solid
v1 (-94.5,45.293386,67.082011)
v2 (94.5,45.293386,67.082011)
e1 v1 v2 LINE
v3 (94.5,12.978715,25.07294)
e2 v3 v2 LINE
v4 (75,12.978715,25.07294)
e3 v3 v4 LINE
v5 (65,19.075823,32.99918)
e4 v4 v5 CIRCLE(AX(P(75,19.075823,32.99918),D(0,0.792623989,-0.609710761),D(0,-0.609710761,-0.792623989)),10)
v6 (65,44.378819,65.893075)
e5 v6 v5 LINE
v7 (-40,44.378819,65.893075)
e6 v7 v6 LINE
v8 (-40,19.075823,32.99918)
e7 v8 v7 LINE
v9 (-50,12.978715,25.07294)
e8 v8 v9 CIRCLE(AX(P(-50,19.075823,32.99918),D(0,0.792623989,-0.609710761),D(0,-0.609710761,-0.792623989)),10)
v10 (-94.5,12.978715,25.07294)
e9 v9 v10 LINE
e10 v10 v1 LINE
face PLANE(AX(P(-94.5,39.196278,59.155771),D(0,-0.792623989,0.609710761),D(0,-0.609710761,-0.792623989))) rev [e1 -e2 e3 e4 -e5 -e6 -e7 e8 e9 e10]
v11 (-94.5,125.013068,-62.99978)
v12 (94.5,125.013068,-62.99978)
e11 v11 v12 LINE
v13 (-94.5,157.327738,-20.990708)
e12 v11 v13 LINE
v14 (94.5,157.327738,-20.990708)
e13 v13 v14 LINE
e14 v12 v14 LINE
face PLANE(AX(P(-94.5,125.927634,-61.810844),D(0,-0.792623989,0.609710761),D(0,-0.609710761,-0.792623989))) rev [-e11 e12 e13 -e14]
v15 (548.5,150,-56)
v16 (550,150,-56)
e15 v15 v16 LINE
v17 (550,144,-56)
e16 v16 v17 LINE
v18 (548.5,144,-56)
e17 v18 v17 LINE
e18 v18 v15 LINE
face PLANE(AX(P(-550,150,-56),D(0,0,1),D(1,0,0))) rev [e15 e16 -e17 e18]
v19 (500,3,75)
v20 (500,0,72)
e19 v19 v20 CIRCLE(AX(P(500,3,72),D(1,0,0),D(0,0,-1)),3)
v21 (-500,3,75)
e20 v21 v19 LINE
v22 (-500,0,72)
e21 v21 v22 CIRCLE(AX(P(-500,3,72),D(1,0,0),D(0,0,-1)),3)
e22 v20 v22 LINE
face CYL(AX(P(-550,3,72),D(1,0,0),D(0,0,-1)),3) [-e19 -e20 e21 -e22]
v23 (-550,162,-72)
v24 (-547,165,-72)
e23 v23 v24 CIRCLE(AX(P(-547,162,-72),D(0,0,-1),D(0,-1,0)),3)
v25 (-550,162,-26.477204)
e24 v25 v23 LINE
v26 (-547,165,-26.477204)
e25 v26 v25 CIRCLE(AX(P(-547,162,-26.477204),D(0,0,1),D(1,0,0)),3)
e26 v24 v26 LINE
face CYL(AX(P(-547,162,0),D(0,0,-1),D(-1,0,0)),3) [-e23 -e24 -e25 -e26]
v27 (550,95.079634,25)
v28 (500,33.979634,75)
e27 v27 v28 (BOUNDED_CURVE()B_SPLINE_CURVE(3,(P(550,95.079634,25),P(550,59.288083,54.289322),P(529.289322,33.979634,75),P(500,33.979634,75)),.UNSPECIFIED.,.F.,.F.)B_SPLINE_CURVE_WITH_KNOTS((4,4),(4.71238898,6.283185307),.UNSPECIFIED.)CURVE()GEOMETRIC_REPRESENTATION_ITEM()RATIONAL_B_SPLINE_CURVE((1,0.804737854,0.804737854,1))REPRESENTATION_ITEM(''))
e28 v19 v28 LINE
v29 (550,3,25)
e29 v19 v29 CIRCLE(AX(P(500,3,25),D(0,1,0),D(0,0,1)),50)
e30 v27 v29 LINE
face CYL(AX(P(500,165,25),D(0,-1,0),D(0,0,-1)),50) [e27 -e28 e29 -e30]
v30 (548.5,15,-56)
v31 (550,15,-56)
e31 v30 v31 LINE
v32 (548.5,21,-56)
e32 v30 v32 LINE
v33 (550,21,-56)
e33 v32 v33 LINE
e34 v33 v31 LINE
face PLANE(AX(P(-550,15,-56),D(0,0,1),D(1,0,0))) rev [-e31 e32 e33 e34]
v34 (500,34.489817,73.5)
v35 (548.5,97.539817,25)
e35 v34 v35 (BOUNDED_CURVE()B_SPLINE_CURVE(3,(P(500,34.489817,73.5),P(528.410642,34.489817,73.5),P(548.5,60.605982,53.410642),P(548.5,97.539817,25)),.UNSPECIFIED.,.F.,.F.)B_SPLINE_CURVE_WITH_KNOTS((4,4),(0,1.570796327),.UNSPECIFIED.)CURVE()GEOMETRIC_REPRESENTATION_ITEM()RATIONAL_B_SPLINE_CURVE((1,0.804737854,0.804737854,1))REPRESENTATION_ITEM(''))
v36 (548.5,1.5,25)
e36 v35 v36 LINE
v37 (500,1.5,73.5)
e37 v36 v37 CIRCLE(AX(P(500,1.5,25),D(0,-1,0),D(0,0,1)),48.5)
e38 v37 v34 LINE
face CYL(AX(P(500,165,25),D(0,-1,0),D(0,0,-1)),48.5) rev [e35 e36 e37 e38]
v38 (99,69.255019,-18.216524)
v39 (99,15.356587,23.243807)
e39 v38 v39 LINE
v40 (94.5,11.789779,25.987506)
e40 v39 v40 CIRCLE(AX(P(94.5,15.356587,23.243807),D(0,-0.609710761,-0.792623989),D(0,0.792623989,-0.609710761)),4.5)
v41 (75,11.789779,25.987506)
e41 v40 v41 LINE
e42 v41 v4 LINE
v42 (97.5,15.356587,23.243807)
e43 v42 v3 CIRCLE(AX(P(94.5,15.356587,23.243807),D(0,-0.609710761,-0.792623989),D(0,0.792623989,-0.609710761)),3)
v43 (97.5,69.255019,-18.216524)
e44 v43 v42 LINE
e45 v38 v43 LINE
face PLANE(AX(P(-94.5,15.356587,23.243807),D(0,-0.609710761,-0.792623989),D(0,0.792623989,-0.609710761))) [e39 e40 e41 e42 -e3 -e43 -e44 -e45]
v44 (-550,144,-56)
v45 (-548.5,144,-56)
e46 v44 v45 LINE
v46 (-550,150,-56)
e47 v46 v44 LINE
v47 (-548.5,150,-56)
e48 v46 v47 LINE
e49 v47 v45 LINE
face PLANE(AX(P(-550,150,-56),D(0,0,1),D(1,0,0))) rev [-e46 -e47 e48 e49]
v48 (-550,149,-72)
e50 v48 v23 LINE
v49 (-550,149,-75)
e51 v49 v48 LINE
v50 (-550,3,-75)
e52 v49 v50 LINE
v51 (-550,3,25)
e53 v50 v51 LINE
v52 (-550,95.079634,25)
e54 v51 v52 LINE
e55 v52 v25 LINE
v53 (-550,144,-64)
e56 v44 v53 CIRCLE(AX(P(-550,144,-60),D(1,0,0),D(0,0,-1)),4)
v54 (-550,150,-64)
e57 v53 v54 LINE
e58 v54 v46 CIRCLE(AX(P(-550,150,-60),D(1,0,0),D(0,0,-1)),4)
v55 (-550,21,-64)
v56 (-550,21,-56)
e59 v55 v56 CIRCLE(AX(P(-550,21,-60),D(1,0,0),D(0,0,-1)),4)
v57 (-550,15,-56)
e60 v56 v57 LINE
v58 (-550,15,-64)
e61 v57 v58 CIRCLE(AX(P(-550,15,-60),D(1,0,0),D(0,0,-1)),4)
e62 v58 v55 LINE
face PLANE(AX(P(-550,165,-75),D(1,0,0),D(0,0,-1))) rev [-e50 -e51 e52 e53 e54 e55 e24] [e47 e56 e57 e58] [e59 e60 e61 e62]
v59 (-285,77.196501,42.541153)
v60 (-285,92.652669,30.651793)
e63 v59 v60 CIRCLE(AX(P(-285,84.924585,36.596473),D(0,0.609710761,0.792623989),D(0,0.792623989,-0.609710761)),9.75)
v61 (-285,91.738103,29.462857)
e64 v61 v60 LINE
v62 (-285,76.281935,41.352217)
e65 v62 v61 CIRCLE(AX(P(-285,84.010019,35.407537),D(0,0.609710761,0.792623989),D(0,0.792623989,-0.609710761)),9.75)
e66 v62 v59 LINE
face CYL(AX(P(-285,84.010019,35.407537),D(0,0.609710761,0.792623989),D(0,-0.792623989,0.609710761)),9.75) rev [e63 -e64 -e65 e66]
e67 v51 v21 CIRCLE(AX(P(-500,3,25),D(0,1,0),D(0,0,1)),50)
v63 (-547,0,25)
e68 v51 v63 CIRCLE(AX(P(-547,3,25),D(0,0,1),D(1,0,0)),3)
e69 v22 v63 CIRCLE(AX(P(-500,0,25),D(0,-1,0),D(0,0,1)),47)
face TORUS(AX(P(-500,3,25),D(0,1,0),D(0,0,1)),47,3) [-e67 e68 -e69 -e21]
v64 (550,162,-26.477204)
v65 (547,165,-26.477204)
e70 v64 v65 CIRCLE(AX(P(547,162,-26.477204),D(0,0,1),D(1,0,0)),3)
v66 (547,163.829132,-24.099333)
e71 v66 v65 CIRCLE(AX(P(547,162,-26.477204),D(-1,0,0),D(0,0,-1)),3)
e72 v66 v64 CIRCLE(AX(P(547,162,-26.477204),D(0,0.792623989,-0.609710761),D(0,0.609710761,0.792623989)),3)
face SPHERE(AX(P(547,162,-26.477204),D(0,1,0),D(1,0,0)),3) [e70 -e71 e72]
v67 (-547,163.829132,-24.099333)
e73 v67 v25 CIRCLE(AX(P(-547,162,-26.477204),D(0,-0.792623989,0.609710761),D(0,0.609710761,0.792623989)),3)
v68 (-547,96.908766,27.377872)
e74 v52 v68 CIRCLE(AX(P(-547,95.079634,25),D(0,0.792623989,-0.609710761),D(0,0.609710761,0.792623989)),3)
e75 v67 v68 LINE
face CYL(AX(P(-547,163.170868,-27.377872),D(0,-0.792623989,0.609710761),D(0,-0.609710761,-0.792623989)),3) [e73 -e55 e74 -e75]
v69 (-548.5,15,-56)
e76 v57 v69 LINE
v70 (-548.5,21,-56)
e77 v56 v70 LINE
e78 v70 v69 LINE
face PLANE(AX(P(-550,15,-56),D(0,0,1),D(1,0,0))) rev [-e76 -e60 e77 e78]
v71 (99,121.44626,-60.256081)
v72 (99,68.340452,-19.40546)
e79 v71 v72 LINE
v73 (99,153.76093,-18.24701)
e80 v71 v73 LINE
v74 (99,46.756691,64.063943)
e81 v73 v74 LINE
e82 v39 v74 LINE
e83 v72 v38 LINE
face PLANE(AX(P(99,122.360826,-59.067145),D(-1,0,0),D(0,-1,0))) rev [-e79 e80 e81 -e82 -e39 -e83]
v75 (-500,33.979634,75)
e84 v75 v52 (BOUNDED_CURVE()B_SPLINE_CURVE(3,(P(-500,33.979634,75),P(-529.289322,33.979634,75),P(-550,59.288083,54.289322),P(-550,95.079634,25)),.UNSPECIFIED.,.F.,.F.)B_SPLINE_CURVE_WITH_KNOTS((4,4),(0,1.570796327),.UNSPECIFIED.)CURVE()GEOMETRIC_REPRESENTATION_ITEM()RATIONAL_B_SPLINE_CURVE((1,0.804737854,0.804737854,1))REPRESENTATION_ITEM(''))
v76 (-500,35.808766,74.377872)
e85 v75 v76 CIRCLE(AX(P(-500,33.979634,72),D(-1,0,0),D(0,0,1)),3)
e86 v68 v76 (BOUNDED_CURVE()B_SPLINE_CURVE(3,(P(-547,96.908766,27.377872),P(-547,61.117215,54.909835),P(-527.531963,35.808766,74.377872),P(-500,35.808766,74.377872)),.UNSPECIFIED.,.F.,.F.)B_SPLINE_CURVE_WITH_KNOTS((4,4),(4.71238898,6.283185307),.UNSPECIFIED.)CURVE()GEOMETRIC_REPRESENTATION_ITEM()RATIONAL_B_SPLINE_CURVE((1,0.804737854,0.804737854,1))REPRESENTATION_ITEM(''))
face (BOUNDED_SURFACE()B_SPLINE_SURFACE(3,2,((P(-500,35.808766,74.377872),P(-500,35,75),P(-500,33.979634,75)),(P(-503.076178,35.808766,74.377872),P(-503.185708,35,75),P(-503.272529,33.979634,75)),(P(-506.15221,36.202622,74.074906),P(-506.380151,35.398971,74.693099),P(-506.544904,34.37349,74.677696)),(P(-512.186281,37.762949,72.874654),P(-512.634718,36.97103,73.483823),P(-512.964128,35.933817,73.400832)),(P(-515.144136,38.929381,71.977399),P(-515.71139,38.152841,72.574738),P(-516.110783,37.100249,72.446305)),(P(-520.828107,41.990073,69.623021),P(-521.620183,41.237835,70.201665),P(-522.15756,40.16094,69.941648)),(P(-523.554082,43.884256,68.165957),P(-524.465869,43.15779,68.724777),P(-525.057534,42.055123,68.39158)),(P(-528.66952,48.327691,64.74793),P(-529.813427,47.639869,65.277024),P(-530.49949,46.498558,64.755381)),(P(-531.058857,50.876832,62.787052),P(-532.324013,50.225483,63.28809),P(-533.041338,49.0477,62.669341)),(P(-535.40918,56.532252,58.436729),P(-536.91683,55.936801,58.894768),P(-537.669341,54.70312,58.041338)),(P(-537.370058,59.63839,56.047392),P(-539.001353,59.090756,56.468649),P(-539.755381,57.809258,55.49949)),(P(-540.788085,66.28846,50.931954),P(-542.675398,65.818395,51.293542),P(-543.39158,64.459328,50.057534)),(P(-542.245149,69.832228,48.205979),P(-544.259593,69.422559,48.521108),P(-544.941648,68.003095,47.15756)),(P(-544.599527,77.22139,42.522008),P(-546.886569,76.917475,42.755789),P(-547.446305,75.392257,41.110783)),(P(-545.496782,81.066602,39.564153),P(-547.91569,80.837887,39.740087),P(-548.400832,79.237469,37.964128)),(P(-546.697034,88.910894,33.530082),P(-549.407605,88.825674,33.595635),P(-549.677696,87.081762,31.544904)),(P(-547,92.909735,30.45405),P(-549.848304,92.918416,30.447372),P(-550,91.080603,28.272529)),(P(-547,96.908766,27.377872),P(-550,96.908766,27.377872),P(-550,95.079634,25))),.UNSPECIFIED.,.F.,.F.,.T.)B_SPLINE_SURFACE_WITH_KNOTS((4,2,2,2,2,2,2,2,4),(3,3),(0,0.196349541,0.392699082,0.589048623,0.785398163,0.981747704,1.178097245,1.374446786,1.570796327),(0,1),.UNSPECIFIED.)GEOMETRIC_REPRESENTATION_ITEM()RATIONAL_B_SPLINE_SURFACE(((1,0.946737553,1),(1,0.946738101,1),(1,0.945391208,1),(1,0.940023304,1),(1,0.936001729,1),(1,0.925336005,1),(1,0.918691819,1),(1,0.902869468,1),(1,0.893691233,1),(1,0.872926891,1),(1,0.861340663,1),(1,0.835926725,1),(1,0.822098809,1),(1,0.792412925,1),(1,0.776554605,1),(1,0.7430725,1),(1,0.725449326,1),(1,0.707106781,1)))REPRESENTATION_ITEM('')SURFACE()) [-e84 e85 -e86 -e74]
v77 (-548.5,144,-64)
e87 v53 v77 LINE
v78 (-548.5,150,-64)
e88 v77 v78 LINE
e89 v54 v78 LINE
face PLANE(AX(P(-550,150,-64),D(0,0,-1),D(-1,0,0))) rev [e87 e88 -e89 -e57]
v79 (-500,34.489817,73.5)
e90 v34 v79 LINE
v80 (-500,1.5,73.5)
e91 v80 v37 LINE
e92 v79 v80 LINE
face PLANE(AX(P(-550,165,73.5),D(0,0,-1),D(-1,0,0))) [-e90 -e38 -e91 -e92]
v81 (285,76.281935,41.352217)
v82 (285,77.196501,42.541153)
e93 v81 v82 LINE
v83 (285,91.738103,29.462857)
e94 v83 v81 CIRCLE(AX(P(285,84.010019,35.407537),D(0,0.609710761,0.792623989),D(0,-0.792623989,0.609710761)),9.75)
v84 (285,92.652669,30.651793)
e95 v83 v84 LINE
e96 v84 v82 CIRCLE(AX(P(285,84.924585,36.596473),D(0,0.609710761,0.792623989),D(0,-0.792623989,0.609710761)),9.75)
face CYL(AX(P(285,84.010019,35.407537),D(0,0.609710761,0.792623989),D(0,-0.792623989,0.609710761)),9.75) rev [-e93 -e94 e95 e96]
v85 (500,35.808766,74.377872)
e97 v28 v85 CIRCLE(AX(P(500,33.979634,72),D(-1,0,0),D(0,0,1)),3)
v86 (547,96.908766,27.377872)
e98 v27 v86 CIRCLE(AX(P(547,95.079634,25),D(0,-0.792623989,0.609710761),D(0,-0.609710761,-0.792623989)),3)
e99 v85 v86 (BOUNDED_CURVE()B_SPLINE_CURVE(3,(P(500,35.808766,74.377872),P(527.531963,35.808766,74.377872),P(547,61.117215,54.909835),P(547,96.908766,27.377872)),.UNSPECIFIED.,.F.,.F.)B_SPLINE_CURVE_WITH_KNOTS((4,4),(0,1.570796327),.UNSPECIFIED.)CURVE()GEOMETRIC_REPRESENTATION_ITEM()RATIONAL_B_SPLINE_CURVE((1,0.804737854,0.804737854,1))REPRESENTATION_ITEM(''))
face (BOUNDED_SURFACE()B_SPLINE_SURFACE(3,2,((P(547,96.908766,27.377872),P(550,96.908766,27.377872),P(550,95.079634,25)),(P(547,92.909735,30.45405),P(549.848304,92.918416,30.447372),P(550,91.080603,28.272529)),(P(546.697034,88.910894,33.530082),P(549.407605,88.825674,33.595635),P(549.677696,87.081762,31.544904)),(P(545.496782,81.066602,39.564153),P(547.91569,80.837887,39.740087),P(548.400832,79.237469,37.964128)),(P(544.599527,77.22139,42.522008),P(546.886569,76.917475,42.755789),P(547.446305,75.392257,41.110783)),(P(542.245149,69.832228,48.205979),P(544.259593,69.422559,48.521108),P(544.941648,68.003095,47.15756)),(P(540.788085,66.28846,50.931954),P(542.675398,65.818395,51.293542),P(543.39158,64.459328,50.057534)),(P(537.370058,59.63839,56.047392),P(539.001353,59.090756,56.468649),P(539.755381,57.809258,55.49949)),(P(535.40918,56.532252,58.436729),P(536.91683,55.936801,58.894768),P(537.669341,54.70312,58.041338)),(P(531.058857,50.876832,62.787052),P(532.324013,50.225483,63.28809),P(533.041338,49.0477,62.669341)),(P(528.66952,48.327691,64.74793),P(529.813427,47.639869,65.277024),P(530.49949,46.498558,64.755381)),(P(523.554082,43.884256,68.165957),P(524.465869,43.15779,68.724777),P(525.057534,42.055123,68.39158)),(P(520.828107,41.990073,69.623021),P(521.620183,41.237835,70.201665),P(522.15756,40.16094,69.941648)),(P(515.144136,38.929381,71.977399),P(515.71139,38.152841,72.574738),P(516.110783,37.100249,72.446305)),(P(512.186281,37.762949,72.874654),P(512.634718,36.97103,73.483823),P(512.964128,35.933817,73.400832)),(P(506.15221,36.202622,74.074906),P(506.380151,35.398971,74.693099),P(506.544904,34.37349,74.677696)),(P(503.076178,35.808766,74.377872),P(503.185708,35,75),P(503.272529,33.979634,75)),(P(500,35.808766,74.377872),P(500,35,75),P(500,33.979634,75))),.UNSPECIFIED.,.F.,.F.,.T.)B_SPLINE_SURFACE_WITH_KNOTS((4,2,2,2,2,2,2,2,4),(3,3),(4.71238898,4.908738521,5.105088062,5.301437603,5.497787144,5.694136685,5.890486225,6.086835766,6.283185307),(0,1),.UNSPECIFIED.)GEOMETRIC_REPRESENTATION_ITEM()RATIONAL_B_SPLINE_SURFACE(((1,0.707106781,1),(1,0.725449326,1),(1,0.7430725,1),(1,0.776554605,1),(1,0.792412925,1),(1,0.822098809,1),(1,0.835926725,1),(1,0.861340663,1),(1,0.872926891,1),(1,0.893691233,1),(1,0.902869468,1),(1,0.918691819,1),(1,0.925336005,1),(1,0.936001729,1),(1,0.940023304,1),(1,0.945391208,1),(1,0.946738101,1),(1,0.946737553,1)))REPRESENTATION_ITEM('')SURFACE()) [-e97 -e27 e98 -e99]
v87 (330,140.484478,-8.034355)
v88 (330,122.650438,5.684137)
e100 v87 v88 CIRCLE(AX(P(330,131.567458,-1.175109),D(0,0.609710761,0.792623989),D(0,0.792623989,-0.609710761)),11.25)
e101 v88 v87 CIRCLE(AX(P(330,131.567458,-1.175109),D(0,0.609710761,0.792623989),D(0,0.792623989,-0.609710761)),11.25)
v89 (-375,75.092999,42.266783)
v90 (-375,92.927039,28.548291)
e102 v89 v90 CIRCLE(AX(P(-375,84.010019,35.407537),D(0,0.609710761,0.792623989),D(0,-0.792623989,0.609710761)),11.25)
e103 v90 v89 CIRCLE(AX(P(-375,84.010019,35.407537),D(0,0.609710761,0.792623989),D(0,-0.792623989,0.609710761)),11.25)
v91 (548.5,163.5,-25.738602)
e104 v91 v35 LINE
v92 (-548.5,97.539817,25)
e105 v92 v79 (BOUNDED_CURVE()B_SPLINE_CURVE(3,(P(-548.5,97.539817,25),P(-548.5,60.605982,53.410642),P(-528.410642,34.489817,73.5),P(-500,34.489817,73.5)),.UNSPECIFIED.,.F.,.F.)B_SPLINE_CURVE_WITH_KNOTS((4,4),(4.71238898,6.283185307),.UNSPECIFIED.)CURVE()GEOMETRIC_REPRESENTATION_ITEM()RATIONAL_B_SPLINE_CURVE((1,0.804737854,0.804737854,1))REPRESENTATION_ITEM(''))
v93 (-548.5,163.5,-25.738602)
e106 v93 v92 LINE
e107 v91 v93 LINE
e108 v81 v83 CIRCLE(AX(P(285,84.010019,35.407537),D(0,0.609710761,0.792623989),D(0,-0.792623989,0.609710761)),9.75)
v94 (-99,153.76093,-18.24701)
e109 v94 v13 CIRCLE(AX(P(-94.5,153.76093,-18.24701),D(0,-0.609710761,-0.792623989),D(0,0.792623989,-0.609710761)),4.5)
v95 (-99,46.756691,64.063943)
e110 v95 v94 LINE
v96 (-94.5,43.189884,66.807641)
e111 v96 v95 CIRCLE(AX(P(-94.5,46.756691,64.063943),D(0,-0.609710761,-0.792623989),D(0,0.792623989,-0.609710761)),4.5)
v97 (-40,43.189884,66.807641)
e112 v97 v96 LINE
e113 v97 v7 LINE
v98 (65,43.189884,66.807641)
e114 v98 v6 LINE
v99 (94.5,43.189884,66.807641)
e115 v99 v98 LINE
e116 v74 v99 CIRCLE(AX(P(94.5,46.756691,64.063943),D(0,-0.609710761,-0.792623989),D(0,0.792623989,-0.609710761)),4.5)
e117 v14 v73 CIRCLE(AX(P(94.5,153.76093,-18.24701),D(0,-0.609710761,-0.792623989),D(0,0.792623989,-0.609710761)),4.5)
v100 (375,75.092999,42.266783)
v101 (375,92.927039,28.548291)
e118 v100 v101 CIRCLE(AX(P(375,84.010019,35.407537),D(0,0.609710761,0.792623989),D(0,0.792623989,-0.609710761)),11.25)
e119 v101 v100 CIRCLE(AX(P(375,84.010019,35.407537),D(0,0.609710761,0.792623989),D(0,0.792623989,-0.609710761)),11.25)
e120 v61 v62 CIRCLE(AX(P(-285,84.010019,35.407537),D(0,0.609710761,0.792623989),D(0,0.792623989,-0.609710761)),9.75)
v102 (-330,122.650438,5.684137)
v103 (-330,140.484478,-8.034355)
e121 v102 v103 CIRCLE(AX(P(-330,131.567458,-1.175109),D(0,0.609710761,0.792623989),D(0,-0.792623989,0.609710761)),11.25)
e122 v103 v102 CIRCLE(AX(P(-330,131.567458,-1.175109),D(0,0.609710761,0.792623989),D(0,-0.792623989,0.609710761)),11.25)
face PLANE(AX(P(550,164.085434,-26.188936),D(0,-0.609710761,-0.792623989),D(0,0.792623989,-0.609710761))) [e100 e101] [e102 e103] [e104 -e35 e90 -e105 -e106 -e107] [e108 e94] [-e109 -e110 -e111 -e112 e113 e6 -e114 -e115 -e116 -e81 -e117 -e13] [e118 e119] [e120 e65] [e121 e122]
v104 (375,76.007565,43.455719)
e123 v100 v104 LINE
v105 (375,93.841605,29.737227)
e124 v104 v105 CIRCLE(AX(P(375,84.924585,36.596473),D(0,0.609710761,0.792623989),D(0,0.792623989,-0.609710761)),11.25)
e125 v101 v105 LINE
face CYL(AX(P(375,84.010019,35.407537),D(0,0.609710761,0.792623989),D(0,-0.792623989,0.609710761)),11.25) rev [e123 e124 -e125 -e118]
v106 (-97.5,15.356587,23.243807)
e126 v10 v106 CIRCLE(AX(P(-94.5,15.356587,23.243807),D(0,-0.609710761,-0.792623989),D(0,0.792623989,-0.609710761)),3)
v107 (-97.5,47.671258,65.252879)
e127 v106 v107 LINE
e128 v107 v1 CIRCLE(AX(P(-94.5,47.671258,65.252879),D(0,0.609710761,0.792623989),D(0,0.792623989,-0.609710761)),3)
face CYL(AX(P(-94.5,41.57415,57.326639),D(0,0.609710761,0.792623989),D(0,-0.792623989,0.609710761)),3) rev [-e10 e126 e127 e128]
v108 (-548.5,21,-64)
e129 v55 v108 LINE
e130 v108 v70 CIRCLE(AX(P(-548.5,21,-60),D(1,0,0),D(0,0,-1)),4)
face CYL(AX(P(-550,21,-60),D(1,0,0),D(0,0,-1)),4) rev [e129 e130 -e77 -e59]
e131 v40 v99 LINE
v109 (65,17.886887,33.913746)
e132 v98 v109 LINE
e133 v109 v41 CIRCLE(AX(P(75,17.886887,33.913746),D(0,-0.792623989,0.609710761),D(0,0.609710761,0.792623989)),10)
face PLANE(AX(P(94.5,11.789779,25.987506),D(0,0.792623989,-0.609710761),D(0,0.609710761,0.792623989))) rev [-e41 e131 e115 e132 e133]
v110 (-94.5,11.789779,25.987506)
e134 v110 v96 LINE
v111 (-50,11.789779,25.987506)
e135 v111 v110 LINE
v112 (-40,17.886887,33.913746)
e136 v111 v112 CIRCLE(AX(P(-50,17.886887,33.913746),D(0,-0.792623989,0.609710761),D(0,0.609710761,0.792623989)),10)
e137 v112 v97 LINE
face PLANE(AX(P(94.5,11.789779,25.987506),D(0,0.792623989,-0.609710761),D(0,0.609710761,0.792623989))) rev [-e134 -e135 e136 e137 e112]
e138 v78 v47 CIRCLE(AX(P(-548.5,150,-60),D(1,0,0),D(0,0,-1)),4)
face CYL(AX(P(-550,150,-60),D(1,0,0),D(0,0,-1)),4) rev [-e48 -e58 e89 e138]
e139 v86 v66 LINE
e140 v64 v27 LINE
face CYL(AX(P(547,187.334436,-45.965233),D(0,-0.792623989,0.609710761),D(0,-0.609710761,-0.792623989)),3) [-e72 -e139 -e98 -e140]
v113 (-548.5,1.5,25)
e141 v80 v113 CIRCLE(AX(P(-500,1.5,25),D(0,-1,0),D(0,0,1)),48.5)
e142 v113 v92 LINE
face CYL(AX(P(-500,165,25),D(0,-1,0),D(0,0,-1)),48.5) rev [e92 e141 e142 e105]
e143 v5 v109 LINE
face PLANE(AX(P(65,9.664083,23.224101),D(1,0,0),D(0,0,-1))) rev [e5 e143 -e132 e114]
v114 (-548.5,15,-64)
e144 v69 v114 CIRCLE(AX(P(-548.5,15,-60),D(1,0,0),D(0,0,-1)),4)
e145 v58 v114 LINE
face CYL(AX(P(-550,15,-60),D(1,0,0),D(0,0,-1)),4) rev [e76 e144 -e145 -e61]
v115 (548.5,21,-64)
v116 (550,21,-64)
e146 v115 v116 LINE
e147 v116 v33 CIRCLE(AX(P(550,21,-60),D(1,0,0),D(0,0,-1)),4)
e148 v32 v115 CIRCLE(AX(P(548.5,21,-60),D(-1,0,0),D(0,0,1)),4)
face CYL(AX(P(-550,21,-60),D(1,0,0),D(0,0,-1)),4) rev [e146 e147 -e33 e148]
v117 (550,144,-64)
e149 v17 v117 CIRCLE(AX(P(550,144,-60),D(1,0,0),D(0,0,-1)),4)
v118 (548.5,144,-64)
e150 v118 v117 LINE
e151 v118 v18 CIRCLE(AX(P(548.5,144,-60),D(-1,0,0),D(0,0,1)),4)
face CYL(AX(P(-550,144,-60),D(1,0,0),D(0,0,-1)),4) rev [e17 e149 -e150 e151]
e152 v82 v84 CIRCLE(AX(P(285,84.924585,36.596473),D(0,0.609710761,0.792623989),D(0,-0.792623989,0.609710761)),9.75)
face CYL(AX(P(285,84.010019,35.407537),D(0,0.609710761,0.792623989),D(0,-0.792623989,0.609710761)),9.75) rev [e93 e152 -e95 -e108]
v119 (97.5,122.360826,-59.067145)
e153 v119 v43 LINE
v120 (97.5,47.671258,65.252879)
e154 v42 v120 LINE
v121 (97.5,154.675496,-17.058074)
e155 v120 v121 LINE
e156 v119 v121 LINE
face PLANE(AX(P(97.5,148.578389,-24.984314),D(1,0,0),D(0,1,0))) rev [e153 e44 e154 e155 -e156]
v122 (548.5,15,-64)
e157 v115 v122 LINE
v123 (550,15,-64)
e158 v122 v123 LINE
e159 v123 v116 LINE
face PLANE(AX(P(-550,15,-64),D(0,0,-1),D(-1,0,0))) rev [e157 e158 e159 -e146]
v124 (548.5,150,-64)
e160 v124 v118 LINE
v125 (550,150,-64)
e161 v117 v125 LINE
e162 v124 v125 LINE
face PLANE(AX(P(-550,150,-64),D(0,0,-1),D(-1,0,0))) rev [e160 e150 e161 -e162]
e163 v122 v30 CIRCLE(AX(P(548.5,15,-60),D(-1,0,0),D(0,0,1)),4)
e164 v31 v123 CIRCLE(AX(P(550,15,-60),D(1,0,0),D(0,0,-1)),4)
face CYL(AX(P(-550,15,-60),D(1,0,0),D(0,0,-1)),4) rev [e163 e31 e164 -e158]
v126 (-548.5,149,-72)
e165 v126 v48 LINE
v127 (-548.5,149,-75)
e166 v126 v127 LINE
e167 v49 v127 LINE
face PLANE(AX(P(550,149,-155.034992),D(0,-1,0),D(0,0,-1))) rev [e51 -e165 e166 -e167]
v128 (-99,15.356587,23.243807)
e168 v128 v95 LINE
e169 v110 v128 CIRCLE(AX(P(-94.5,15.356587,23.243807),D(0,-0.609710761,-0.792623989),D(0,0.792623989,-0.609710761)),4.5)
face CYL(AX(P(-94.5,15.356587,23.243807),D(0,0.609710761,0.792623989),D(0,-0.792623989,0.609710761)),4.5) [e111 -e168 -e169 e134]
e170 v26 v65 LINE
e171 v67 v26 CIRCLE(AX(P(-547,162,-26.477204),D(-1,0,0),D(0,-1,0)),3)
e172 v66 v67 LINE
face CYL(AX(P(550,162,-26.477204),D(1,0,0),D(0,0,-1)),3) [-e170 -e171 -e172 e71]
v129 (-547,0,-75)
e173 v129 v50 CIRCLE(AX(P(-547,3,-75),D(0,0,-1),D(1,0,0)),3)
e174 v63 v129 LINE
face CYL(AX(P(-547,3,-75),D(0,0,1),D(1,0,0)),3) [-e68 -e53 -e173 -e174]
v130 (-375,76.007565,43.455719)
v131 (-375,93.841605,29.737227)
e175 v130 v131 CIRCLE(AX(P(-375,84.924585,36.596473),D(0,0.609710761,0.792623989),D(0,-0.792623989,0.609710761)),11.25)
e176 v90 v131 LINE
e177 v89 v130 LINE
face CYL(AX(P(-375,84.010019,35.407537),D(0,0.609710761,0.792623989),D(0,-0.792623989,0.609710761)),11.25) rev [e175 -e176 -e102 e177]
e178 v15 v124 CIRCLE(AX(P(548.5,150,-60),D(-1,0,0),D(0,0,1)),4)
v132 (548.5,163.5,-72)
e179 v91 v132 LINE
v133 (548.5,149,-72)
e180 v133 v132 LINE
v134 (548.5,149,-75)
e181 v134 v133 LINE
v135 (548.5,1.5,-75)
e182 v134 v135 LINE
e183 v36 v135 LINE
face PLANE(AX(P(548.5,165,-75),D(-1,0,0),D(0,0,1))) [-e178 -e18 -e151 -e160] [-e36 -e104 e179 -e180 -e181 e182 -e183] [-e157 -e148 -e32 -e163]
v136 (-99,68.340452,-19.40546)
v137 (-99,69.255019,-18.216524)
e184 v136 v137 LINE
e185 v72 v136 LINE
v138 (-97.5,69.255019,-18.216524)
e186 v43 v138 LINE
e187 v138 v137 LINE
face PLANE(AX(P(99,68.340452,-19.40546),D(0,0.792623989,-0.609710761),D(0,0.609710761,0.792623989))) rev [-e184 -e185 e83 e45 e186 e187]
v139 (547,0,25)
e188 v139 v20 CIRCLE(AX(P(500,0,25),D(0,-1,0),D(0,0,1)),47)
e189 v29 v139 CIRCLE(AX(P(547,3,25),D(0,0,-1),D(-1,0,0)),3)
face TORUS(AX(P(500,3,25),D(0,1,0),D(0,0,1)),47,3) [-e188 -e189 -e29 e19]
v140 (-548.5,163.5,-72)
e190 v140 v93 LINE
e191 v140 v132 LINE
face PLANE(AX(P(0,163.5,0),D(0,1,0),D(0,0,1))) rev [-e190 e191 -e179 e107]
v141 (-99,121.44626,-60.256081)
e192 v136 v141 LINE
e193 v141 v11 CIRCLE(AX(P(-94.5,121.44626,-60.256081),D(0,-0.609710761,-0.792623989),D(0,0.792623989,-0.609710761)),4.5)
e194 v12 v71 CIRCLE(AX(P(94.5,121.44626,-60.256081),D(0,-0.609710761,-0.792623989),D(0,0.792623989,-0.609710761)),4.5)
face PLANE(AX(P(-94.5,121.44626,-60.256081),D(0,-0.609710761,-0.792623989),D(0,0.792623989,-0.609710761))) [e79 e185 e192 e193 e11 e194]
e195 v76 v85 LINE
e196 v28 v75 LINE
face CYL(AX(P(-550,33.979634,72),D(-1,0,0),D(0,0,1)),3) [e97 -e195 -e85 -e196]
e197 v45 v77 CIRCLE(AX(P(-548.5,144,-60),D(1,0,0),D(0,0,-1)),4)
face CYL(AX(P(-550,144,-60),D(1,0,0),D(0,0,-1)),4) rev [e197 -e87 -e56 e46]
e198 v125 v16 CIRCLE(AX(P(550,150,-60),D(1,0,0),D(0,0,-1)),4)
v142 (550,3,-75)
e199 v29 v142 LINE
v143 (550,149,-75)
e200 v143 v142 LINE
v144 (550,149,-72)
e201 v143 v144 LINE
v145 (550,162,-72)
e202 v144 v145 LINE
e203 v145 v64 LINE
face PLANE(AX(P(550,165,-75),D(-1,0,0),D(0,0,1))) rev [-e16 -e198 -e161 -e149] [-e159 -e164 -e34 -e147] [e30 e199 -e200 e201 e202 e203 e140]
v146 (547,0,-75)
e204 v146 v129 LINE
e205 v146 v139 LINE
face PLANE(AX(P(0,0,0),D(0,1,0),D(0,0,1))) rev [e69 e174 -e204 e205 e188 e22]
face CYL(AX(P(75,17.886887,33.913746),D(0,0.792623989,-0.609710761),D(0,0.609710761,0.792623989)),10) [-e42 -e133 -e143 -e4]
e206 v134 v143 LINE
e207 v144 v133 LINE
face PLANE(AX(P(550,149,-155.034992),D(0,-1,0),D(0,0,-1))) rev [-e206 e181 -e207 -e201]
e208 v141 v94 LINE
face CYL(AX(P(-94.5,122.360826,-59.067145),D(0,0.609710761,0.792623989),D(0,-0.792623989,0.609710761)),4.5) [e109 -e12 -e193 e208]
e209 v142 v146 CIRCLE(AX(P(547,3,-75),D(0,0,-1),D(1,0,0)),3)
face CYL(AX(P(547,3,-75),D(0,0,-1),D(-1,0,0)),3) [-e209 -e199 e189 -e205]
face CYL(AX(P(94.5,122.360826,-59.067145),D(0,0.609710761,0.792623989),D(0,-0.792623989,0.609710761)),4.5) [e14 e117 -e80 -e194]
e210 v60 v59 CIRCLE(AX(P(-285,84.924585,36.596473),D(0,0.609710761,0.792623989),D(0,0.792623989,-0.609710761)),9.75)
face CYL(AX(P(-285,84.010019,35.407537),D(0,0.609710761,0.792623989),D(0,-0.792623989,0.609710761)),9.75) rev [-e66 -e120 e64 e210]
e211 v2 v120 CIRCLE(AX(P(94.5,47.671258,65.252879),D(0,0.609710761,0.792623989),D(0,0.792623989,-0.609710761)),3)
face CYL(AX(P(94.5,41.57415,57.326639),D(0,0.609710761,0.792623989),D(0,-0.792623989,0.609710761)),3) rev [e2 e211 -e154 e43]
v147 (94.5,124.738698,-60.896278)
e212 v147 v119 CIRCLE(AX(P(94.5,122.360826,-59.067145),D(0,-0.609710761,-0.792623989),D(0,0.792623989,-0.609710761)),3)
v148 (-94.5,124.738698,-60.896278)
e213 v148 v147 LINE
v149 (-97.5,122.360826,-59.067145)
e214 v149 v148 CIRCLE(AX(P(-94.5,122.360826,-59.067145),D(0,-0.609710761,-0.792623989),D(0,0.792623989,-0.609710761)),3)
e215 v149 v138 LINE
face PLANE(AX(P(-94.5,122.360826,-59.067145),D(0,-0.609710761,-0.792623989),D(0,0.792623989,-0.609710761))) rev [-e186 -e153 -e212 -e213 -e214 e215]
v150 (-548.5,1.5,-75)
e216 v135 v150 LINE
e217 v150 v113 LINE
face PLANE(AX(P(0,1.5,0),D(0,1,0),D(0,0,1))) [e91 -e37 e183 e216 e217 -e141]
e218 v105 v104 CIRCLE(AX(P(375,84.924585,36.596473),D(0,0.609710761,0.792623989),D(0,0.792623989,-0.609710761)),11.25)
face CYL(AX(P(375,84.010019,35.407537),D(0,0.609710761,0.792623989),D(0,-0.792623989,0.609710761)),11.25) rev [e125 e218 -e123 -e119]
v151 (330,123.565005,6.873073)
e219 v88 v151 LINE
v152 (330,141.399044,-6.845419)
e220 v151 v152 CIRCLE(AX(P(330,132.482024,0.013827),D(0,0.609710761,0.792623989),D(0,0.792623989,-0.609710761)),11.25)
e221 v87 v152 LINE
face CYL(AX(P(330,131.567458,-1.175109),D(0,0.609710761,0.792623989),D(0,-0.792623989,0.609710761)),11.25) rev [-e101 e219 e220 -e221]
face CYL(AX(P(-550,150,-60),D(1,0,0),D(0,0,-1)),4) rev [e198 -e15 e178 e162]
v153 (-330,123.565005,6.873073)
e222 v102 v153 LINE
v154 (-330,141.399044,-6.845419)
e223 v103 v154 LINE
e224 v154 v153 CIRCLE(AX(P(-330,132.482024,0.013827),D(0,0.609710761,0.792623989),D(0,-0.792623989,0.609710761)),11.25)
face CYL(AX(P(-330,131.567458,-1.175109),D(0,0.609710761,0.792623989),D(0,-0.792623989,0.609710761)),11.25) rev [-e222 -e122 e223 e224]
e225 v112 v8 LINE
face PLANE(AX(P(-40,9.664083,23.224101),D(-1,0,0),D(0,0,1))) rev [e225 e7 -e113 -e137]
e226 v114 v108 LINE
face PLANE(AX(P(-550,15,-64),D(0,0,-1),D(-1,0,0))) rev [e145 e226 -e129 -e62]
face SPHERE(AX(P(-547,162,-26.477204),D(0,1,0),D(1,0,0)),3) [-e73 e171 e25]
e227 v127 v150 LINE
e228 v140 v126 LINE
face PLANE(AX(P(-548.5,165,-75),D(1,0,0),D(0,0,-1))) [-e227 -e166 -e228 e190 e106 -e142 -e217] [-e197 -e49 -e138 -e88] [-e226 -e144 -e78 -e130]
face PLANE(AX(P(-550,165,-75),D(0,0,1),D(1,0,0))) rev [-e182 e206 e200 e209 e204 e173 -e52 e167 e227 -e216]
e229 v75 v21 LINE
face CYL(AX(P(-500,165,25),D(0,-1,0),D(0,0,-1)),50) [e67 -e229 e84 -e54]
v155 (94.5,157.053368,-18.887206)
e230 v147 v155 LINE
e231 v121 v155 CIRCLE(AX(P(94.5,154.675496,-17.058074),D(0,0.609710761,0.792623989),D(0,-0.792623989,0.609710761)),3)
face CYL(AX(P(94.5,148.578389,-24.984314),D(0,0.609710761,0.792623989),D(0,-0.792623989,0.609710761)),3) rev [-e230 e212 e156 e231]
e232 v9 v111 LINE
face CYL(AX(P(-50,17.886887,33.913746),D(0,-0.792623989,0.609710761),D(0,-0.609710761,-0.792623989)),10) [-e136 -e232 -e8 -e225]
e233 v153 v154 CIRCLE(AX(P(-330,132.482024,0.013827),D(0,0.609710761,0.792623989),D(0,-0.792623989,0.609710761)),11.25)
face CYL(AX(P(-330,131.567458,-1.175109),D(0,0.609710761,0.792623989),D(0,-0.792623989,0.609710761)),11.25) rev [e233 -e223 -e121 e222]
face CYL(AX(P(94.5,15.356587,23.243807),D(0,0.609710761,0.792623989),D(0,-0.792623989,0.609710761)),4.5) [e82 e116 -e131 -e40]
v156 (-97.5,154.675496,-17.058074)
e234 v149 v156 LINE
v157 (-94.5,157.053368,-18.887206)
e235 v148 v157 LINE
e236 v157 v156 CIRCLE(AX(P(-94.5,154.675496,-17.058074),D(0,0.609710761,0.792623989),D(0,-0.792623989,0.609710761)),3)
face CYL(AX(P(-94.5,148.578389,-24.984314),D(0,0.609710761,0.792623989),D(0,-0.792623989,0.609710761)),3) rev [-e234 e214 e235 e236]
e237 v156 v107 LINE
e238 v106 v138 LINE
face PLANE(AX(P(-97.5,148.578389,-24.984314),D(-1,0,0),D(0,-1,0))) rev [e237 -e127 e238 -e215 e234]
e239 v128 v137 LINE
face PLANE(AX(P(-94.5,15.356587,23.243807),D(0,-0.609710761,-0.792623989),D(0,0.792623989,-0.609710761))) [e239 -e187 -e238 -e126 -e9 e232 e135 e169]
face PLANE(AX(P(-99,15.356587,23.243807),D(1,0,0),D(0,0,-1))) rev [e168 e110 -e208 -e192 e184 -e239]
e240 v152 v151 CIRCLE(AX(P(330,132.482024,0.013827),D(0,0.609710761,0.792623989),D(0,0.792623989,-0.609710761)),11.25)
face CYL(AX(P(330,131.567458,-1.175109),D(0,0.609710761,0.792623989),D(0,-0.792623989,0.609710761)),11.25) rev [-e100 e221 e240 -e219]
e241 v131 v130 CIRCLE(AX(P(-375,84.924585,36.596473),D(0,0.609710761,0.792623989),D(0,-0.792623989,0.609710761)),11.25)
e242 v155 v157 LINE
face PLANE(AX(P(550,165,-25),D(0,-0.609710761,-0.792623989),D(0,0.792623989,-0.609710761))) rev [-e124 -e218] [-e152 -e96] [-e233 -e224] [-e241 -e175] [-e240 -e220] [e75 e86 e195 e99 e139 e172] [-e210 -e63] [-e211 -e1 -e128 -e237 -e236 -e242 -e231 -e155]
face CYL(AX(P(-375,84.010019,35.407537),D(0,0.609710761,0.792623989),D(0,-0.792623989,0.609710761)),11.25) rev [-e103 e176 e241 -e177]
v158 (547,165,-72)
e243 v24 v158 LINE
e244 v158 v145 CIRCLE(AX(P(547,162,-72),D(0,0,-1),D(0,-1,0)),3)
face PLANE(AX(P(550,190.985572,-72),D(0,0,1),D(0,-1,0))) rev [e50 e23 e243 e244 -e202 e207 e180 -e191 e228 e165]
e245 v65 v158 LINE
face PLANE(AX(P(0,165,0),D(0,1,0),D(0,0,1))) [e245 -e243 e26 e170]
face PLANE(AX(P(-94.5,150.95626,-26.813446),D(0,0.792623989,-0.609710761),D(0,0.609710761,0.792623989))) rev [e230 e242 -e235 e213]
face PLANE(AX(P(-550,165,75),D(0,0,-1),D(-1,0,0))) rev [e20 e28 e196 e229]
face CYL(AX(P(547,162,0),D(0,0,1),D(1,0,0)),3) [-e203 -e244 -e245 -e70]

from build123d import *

# Parameters (mm, degrees)
SKETCH_1_W            = 1100
SKETCH_1_H            = 150
EXTRUDE_1_DEPTH       = 165
CUT_EXTRUDE_8_DEPTH   = 1115.831825882
FILLET_2_R            = 50
SHELL_1_T             = -1.5
HOLE_WIZARD_8_0_8_1_D = 8
SKETCH_20_W           = 83.034991693
SKETCH_20_H           = 41.985572191
CUT_EXTRUDE_7_DEPTH   = 1115.831825882
FILLET_5_R            = 3
CUT_EXTRUDE_10_DEPTH  = 1115.831825988
CUT_EXTRUDE_11_DEPTH  = 10
EXTRUDE_2_DEPTH       = 51.5
EXTRUDE_3_DEPTH       = 1.5
SKETCH_27_W           = 130
SKETCH_27_H           = 54.986401043
CUT_EXTRUDE_12_DEPTH  = 1.5
MOVE_FACE_1_BY        = 25
FILLET_6_R            = 10
SKETCH_28_R           = 11.25
SKETCH_28_R_2         = 9.75
CUT_EXTRUDE_13_DEPTH  = 1.5


with BuildPart() as part:
    # 草图1 → 凸台-拉伸1 (new body)
    with BuildSketch(Plane(origin=(0, 0, 0), x_dir=(1, 0, 0), z_dir=(0, 1, 0))):
        Rectangle(SKETCH_1_W, SKETCH_1_H)
    extrude(amount=EXTRUDE_1_DEPTH)

    # 草图21 → 切除-拉伸8 (cut, through all)
    with BuildSketch(Plane.ZY.offset(550)):
        Polygon((-25, 165), (75, 35), (149.01608628, 35), (149.01608628, 165), align=None)
    extrude(amount=-CUT_EXTRUDE_8_DEPTH, mode=Mode.SUBTRACT)

    # 圆角2
    fillet_2_edges = [part.edges().sort_by_distance(p)[0] for p in [
        (550, 17.5, 75),
        (-550, 17.5, 75),
    ]]
    fillet(fillet_2_edges, radius=FILLET_2_R)

    # 抽壳1
    shell_1_openings = [part.faces().sort_by_distance(p)[0] for p in [
        (0, 82.5, -75),
    ]]
    offset(amount=SHELL_1_T, openings=shell_1_openings, kind=Kind.INTERSECTION)

    # Ø8.0 (8) 直径孔1 (through all)
    with Locations(Plane.ZY.offset(550)):
        with Locations((-60, 147), (-60, 18)):
            Hole(HOLE_WIZARD_8_0_8_1_D / 2)

    # 草图20 → 切除-拉伸7 (cut, through all)
    with BuildSketch(Plane.ZY.offset(550)):
        with Locations((-113.517495847, 169.992786096)):
            Rectangle(SKETCH_20_W, SKETCH_20_H)
    extrude(amount=-CUT_EXTRUDE_7_DEPTH, mode=Mode.SUBTRACT)

    # 圆角5
    fillet_5_edges = [part.edges().sort_by_distance(p)[0] for p in [
        (550, 165, -48.5),
        (0, 165, -25),
        (-550, 132.5, 0),
        (550, 132.5, 0),
        (550, 0, -25),
        (0, 0, 75),
        (-535.355339059, 0, 60.355339059),
        (535.355339059, 0, 60.355339059),
        (0, 35, 75),
        (-539.140260323, 59.552655996, 56.113341541),
        (539.140260323, 59.552655996, 56.113341541),
        (-550, 0, -25),
        (-550, 165, -48.5),
    ]]
    fillet(fillet_5_edges, radius=FILLET_5_R)

    # 草图23 → 切除-拉伸10 (cut, through all)
    with BuildSketch(Plane(origin=(550, 0, 0), x_dir=(0, 0, -1), z_dir=(1, 0, 0))):
        with BuildLine():
            Line((64, 150), (64, 144))
            ThreePointArc((64, 144), (60, 140), (56, 144))
            Line((56, 144), (56, 150))
            ThreePointArc((56, 150), (60, 154), (64, 150))
        make_face()
        with BuildLine():
            Line((56, 15), (56, 21))
            ThreePointArc((56, 21), (60, 25), (64, 21))
            Line((64, 21), (64, 15))
            ThreePointArc((64, 15), (60, 11), (56, 15))
        make_face()
    extrude(amount=-CUT_EXTRUDE_10_DEPTH, mode=Mode.SUBTRACT)

    # 草图24 → 切除-拉伸11 (cut)
    with BuildSketch(Plane(origin=(0, 49.256505576, 64.033457249), x_dir=(1, 0, 0), z_dir=(0, 0.6097107608496924, 0.7926239891046002))):
        with BuildLine():
            Line((-94.5, 136), (94.5, 136))
            ThreePointArc((94.5, 136), (96.621320344, 135.121320344), (97.5, 133))
            Line((97.5, 133), (97.5, -2))
            ThreePointArc((97.5, -2), (96.621320344, -4.121320344), (94.5, -5))
            Line((94.5, -5), (-94.5, -5))
            ThreePointArc((-94.5, -5), (-96.621320344, -4.121320344), (-97.5, -2))
            Line((-97.5, -2), (-97.5, 133))
            ThreePointArc((-97.5, 133), (-96.621320344, 135.121320344), (-94.5, 136))
        make_face()
    extrude(amount=-CUT_EXTRUDE_11_DEPTH, mode=Mode.SUBTRACT)

    # 草图25 → 凸台-拉伸2 (add)
    with BuildSketch(Plane(origin=(0, 48.341939435, 62.844521265), x_dir=(-1, 0, 0), z_dir=(0, -0.6097107608496924, -0.7926239891046002))):
        with BuildLine():
            Line((99, -2), (99, 133))
            ThreePointArc((99, 133), (97.681980515, 136.181980515), (94.5, 137.5))
            Line((94.5, 137.5), (-94.5, 137.5))
            ThreePointArc((-94.5, 137.5), (-97.681980515, 136.181980515), (-99, 133))
            Line((-99, 133), (-99, -2))
            ThreePointArc((-99, -2), (-97.681980515, -5.181980515), (-94.5, -6.5))
            Line((-94.5, -6.5), (94.5, -6.5))
            ThreePointArc((94.5, -6.5), (97.681980515, -5.181980515), (99, -2))
        make_face()
        with BuildLine():
            Line((94.5, 136), (-94.5, 136))
            ThreePointArc((-94.5, 136), (-96.621320344, 135.121320344), (-97.5, 133))
            Line((-97.5, 133), (-97.5, -2))
            ThreePointArc((-97.5, -2), (-96.621320344, -4.121320344), (-94.5, -5))
            Line((-94.5, -5), (94.5, -5))
            ThreePointArc((94.5, -5), (96.621320344, -4.121320344), (97.5, -2))
            Line((97.5, -2), (97.5, 133))
            ThreePointArc((97.5, 133), (96.621320344, 135.121320344), (94.5, 136))
        make_face(mode=Mode.SUBTRACT)
    extrude(amount=EXTRUDE_2_DEPTH)

    # 草图26 → 凸台-拉伸3 (add)
    with BuildSketch(Plane(origin=(0, 16.941835251, 22.024385827), x_dir=(-1, 0, 0), z_dir=(0, -0.6097107608496924, -0.7926239891046002))):
        with BuildLine():
            Line((-99, 66), (99, 66))
            Line((99, 66), (99, 133))
            ThreePointArc((99, 133), (97.681980515, 136.181980515), (94.5, 137.5))
            Line((94.5, 137.5), (-94.5, 137.5))
            ThreePointArc((-94.5, 137.5), (-97.681980515, 136.181980515), (-99, 133))
            Line((-99, 133), (-99, 66))
        make_face()
    extrude(amount=EXTRUDE_3_DEPTH)

    # 草图27 → 切除-拉伸12 (cut)
    with BuildSketch(Plane(origin=(0, -3.963119946, 3.048553804), x_dir=(1, 0, 0), z_dir=(0, 0.7926239891046, -0.6097107608496924))):
        with Locations((0, -51.793475292)):
            Rectangle(SKETCH_27_W, SKETCH_27_H)
    extrude(amount=-CUT_EXTRUDE_12_DEPTH, mode=Mode.SUBTRACT)

    # Move Face 1: a face moved outward by 25.0
    extrude(part.faces().sort_by_distance((-65, 28.084299406, 45.940290421))[0], amount=MOVE_FACE_1_BY, dir=(1, 0, 0))

    # 圆角6
    fillet_6_edges = [part.edges().sort_by_distance(p)[0] for p in [
        (65, 12.384247314, 25.530222701),
        (-40, 12.384247314, 25.530222701),
    ]]
    fillet(fillet_6_edges, radius=FILLET_6_R)

    # 草图28 → 切除-拉伸13 (cut)
    with BuildSketch(Plane(origin=(0, 49.256505576, 64.033457249), x_dir=(1, 0, 0), z_dir=(0, 0.6097107608496924, 0.7926239891046))):
        with Locations(Location((-330, 105, 0), (0, 0, 270))):
            Circle(SKETCH_28_R)
        with Locations(Location((330, 105, 0), (0, 0, 270))):
            Circle(SKETCH_28_R)
        with Locations(Location((375, 45, 0), (0, 0, 270))):
            Circle(SKETCH_28_R)
        with Locations(Location((285, 45, 0), (0, 0, 270))):
            Circle(SKETCH_28_R_2)
        with Locations(Location((-285, 45, 0), (0, 0, 270))):
            Circle(SKETCH_28_R_2)
        with Locations(Location((-375, 45, 0), (0, 0, 270))):
            Circle(SKETCH_28_R)
    extrude(amount=-CUT_EXTRUDE_13_DEPTH, mode=Mode.SUBTRACT)


solid = part.part
